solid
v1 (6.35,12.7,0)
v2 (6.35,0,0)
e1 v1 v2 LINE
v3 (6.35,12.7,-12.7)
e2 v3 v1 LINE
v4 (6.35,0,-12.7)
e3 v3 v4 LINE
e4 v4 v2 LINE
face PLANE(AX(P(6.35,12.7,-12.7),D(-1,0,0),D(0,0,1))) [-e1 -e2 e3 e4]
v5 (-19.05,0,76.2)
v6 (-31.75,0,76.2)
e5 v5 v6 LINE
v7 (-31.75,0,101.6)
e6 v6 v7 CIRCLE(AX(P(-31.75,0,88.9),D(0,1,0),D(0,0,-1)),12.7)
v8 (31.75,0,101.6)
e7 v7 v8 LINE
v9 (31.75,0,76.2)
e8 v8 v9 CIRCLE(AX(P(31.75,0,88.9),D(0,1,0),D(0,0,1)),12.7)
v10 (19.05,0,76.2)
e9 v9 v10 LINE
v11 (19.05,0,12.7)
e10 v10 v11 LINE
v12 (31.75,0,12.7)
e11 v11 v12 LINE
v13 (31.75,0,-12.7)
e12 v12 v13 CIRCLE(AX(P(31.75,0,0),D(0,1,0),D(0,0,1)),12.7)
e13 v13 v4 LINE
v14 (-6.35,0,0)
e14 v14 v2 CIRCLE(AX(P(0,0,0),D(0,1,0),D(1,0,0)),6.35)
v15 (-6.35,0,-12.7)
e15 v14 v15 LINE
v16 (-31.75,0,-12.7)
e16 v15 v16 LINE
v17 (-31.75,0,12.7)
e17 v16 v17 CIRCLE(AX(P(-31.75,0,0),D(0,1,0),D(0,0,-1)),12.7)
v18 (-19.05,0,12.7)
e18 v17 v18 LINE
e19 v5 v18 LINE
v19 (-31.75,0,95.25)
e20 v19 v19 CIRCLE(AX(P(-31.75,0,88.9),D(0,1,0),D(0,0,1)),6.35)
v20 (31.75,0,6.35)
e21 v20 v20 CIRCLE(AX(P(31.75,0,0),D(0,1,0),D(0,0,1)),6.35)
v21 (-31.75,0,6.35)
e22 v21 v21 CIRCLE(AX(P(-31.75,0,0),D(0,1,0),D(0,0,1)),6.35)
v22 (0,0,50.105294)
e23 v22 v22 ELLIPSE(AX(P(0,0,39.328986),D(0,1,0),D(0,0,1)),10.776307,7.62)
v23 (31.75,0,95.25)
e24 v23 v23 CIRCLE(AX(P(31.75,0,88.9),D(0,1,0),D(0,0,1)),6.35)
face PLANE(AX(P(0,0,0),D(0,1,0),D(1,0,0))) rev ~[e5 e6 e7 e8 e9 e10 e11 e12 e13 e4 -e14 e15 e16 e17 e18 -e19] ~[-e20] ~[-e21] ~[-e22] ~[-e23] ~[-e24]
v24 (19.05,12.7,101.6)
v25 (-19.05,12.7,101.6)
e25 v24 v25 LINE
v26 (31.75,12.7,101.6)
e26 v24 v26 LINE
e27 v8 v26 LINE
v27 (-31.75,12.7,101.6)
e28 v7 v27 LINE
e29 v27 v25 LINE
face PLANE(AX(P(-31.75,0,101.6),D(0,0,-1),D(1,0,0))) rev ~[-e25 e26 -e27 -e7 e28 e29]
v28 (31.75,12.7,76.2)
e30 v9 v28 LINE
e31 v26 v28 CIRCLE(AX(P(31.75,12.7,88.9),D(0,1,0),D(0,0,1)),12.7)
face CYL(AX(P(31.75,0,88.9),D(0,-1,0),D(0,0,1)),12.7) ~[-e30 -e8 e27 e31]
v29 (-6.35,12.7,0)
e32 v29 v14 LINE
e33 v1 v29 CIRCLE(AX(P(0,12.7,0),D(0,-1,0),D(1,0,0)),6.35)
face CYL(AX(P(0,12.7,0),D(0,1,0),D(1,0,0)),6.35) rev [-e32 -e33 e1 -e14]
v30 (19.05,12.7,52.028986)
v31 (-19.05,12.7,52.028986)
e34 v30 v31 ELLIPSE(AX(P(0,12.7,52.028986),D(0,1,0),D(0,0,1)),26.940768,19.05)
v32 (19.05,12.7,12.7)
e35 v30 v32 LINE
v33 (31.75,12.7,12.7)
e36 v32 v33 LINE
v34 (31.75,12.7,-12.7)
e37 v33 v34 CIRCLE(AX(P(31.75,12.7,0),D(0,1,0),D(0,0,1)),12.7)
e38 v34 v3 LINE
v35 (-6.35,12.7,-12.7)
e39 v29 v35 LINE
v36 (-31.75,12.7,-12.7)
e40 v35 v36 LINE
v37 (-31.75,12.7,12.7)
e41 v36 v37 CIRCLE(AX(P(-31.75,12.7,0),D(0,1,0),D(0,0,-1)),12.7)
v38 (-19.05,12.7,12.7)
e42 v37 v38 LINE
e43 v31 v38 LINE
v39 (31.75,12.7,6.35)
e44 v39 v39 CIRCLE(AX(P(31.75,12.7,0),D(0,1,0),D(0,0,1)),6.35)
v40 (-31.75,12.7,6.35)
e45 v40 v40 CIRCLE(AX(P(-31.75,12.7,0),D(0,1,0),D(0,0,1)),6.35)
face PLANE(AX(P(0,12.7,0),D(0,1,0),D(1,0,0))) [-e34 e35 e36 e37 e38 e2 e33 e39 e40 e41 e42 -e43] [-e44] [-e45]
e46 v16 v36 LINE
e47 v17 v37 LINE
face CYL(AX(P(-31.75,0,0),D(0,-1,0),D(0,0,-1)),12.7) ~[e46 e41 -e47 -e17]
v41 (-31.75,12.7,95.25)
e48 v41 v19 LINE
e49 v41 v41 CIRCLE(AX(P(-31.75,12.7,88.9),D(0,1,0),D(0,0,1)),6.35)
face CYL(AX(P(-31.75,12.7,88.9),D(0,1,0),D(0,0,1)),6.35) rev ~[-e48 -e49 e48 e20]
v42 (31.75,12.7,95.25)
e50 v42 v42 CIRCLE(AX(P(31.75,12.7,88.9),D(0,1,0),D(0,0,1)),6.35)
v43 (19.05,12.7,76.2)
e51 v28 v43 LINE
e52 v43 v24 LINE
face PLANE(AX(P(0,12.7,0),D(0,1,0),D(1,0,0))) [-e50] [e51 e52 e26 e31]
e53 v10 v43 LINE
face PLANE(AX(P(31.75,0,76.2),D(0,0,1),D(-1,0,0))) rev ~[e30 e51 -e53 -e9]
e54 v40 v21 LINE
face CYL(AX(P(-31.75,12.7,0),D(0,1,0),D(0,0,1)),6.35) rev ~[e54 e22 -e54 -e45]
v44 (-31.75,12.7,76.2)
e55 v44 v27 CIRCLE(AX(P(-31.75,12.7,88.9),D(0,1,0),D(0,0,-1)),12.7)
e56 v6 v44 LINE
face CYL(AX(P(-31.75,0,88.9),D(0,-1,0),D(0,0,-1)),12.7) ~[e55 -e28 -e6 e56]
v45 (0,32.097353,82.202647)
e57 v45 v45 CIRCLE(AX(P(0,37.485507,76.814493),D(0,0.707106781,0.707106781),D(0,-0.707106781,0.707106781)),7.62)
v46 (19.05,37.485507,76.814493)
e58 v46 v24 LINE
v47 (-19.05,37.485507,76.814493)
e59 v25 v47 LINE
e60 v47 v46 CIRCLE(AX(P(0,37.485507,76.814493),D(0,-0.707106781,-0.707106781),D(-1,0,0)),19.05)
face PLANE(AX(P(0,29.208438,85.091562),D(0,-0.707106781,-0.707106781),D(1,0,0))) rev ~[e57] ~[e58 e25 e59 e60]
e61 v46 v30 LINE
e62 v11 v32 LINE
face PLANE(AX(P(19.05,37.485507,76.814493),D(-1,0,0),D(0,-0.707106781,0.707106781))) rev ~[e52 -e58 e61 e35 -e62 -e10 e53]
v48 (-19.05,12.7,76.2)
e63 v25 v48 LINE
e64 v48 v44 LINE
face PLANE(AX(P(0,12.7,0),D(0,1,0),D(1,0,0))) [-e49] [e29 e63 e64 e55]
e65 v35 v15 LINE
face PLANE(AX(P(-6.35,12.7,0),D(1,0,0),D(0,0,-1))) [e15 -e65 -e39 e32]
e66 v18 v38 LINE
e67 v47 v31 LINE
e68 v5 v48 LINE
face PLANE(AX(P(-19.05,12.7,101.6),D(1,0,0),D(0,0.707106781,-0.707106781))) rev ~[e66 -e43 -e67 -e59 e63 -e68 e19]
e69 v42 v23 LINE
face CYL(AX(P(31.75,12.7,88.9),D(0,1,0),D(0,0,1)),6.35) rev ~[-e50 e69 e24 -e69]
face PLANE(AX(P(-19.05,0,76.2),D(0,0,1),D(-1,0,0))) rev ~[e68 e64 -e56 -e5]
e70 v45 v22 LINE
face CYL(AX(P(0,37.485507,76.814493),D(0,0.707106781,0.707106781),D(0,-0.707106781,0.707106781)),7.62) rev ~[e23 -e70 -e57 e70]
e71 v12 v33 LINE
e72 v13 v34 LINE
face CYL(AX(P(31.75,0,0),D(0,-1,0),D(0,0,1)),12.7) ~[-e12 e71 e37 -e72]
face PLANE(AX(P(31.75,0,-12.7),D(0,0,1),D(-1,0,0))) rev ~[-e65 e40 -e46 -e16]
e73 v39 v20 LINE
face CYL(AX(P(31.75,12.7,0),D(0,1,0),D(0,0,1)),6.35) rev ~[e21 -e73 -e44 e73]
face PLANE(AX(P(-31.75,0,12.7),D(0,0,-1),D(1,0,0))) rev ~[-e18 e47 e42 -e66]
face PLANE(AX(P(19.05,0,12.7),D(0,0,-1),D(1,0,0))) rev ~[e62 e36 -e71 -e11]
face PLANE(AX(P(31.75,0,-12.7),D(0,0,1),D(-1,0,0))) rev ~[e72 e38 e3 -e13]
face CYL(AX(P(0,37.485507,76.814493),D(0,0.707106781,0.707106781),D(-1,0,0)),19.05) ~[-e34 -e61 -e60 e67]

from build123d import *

# Parameters (mm, degrees)
BASE_PLATE_SKETCH_W     = 38.1
BASE_PLATE_SKETCH_H     = 63.5
BASE_PLATE_DEPTH        = 12.7
MOUNTING_HOLES_SKETCH_R = 6.35
MOUNTING_HOLES_DEPTH    = 112.622813528
INCLINED_LUG_REACH      = 102.603
LUG_BORE_REACH          = 102.603
LUG_BORE_SKETCH_R       = 7.62


with BuildPart() as part:
    # Base Plate Sketch → Base Plate (new body)
    with BuildSketch(Plane(origin=(0, 0, 0), x_dir=(1, 0, 0), z_dir=(0, 1, 0))):
        with BuildLine():
            Line((31.75, 12.7), (-31.75, 12.7))
            ThreePointArc((-31.75, 12.7), (-44.45, 0), (-31.75, -12.7))
            Line((-31.75, -12.7), (31.75, -12.7))
            ThreePointArc((31.75, -12.7), (44.45, 0), (31.75, 12.7))
        make_face()
        with Locations((0, -44.45)):
            Rectangle(BASE_PLATE_SKETCH_W, BASE_PLATE_SKETCH_H)
        with BuildLine():
            Line((31.75, -76.2), (-31.75, -76.2))
            ThreePointArc((-31.75, -76.2), (-44.45, -88.9), (-31.75, -101.6))
            Line((-31.75, -101.6), (31.75, -101.6))
            ThreePointArc((31.75, -101.6), (44.45, -88.9), (31.75, -76.2))
        make_face()
    extrude(amount=BASE_PLATE_DEPTH)

    # Mounting Holes Sketch → Mounting Holes (cut, through all)
    with BuildSketch(Plane(origin=(0, 12.7, 0), x_dir=(1, 0, 0), z_dir=(0, 1, 0))):
        with Locations(Location((-31.75, 0, 0), (0, 0, 270))):
            Circle(MOUNTING_HOLES_SKETCH_R)
        with Locations(Location((31.75, 0, 0), (0, 0, 270))):
            Circle(MOUNTING_HOLES_SKETCH_R)
        with Locations(Location((-31.75, -88.9, 0), (0, 0, 270))):
            Circle(MOUNTING_HOLES_SKETCH_R)
        with Locations(Location((31.75, -88.9, 0), (0, 0, 270))):
            Circle(MOUNTING_HOLES_SKETCH_R)
        with BuildLine():
            Line((-6.35, 0), (-6.35, 12.7))
            Line((-6.35, 12.7), (6.35, 12.7))
            Line((6.35, 12.7), (6.35, 0))
            ThreePointArc((6.35, 0), (0, -6.35), (-6.35, 0))
        make_face()
    extrude(amount=-MOUNTING_HOLES_DEPTH, mode=Mode.SUBTRACT)

    # Inclined Lug Sketch → Inclined Lug (add, up to next)
    with BuildSketch(Plane(origin=(0, 57.15, 57.15), x_dir=(-1, 0, 0), z_dir=(0, 0.7071067811865488, 0.7071067811865464)), mode=Mode.PRIVATE) as inclined_lug_sk1:
        with BuildLine():
            Line((-19.05, 62.861792847), (19.05, 62.861792847))
            Line((19.05, 62.861792847), (19.05, 27.809792847))
            ThreePointArc((19.05, 27.809792847), (0, 8.759792847), (-19.05, 27.809792847))
            Line((-19.05, 27.809792847), (-19.05, 62.861792847))
        make_face()
    inclined_lug_tool1 = extrude(inclined_lug_sk1.sketch, amount=-INCLINED_LUG_REACH, mode=Mode.PRIVATE) - part.part
    add(inclined_lug_tool1.solids().sort_by_distance((0, 30.51036, 83.78964))[0])

    # Lug Bore: up to this plane
    lug_bore_end = Plane(origin=(0, 0, 0), z_dir=(0, 1, 0))
    # Lug Bore Sketch → Lug Bore (cut, up to the surface)
    with BuildSketch(Plane(origin=(0, 57.15, 57.15), x_dir=(1, 0, 0), z_dir=(0, 0.7071067811865487, 0.7071067811865465)), mode=Mode.PRIVATE) as lug_bore_sk1:
        with Locations(Location((0, -27.809792847, 0), (0, 0, 270))):
            Circle(LUG_BORE_SKETCH_R)
    lug_bore_tool1 = split(extrude(lug_bore_sk1.sketch, amount=-LUG_BORE_REACH, mode=Mode.PRIVATE), bisect_by=lug_bore_end, keep=Keep.BOTH, mode=Mode.PRIVATE)
    add(lug_bore_tool1.solids().sort_by_distance((0, 37.485507, 76.814493))[0], mode=Mode.SUBTRACT)


solid = part.part
